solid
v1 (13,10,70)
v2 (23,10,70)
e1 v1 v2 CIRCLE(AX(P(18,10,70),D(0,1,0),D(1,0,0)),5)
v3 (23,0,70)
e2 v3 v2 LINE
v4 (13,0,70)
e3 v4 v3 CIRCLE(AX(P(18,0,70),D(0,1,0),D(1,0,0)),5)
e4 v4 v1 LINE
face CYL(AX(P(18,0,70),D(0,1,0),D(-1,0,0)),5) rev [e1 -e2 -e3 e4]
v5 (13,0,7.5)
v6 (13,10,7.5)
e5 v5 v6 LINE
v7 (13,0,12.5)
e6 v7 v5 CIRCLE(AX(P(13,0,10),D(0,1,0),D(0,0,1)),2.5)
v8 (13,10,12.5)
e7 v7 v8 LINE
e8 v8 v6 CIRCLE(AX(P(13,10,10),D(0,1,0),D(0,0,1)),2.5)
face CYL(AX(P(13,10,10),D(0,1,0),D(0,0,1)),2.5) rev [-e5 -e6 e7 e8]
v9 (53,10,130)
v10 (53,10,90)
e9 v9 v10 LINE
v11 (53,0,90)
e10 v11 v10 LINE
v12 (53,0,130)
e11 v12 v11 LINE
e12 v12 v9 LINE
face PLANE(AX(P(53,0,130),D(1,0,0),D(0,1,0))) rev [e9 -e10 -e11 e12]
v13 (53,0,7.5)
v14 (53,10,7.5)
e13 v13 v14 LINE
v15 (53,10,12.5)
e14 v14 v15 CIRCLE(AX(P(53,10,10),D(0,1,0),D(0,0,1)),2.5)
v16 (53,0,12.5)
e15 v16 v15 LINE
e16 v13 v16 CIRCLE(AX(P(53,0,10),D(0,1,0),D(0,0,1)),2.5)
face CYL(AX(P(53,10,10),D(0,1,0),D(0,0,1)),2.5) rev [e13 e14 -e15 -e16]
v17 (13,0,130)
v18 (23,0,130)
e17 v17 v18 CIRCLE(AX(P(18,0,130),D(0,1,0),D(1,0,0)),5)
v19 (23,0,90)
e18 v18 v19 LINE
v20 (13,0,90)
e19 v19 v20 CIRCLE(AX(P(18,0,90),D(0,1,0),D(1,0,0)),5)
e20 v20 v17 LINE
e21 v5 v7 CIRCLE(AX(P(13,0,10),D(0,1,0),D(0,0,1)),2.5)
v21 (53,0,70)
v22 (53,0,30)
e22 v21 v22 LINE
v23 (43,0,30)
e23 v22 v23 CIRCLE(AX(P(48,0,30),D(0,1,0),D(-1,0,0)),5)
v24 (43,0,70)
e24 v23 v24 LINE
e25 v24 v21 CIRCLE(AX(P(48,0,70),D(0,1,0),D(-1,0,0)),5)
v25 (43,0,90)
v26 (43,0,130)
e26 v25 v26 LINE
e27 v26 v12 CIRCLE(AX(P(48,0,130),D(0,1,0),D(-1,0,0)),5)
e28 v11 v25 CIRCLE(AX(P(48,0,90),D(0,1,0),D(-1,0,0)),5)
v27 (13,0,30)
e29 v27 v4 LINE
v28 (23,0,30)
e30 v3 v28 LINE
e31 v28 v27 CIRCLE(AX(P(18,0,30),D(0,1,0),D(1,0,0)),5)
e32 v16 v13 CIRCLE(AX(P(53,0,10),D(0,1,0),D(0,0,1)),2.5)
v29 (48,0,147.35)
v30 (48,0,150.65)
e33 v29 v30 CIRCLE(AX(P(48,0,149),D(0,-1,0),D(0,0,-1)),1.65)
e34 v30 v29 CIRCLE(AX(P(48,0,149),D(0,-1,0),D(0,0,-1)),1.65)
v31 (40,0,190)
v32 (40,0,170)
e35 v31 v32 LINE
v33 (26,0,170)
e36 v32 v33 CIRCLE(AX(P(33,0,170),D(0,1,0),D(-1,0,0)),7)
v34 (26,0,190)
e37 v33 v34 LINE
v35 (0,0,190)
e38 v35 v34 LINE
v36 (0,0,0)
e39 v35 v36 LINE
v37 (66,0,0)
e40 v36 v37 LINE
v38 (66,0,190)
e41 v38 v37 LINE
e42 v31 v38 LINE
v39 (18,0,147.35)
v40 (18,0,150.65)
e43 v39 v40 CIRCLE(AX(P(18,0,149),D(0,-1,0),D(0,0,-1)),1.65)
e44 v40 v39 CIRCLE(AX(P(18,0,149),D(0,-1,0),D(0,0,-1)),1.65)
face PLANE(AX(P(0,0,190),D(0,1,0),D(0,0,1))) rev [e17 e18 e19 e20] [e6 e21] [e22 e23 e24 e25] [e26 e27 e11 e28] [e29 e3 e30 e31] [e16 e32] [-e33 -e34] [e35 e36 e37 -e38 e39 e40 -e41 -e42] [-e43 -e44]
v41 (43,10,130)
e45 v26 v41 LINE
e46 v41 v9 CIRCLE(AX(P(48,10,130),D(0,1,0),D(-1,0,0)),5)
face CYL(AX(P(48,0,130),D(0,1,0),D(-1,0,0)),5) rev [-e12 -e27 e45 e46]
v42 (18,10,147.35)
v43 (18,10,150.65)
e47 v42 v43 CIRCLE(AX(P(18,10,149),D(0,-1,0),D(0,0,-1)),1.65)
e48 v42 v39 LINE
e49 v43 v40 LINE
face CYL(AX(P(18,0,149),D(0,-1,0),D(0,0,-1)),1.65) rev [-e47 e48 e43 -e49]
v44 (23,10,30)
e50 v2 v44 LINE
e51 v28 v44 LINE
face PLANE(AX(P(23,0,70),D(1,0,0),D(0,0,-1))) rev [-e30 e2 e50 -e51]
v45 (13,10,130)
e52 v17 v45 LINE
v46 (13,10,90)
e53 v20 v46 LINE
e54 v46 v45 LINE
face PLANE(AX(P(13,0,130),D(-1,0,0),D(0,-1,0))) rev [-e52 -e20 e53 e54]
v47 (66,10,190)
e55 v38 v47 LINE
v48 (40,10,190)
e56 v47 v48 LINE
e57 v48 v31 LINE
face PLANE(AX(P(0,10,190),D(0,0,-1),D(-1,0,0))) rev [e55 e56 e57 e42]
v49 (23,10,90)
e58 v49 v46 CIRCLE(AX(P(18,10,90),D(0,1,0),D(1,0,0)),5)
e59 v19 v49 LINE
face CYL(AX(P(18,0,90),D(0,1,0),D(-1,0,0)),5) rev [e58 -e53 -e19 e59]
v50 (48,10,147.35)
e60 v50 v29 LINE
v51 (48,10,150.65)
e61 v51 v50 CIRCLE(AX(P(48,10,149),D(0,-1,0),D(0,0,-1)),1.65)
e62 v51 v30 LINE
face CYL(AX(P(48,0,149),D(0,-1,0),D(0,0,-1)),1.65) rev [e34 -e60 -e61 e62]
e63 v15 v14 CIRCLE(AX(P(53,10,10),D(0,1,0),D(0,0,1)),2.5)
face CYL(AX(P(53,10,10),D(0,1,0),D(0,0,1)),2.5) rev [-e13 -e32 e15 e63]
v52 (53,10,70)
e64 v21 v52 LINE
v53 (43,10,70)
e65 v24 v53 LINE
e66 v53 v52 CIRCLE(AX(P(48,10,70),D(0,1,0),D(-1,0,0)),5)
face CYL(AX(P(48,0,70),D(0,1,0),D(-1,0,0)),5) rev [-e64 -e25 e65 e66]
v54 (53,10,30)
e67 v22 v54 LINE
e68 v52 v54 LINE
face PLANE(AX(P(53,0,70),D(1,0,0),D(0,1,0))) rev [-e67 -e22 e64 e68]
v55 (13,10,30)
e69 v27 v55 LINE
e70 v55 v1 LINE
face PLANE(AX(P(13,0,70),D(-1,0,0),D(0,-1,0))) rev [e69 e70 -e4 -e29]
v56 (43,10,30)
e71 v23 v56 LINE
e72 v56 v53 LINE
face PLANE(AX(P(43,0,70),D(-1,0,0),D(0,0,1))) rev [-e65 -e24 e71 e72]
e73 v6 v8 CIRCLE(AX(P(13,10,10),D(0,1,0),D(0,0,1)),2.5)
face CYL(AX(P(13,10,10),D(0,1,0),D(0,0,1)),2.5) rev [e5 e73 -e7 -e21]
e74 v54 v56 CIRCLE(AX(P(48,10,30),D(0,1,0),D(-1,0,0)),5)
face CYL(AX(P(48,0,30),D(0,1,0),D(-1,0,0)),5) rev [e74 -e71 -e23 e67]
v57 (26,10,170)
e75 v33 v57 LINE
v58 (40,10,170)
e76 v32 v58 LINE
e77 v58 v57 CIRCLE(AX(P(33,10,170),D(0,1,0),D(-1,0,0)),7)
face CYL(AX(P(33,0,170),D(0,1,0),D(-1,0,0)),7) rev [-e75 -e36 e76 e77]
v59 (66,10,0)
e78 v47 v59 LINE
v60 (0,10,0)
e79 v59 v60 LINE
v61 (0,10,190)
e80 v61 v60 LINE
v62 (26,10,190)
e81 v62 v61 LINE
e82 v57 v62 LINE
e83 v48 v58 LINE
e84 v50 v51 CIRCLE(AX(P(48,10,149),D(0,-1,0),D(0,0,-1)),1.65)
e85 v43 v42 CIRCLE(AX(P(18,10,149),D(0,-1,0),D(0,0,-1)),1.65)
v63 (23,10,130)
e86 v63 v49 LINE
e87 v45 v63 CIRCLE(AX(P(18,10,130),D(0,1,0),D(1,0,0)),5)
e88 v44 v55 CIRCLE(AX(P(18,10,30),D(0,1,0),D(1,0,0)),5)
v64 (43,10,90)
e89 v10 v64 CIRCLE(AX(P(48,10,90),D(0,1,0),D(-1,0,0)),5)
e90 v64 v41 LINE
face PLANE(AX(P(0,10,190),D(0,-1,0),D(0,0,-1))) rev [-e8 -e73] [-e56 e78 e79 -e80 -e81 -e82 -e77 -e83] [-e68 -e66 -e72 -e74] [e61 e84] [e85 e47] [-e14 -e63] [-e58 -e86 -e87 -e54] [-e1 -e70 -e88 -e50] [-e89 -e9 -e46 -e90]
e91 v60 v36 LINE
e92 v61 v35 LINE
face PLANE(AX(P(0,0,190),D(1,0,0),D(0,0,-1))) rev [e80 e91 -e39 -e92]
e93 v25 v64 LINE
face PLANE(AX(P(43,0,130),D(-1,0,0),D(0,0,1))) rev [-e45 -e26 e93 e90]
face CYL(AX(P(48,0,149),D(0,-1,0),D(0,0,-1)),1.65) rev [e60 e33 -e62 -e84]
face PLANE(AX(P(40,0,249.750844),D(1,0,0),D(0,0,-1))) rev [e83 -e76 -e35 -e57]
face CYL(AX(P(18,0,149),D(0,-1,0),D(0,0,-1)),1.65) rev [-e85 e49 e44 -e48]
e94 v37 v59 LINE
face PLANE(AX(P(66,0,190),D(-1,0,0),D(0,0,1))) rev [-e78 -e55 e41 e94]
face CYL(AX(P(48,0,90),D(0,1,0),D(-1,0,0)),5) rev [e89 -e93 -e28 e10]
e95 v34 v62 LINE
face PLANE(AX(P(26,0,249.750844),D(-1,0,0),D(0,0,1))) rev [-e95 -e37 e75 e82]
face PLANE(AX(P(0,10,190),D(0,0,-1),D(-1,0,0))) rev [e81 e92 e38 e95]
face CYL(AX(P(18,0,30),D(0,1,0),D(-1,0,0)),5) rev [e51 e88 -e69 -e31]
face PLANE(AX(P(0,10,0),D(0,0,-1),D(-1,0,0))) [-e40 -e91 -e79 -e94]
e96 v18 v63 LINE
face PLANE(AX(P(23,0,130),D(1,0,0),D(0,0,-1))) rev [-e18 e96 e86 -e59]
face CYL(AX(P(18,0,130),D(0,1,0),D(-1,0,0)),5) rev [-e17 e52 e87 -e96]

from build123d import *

# Parameters (mm, degrees)
SKETCH_1_W          = 66
SKETCH_1_H          = 10
EXTRUDE_1_DEPTH     = 190
CUT_EXTRUDE_2_DEPTH = 202.385203031
HOLE_WIZARD_M5_1_D  = 5
CUT_EXTRUDE_3_DEPTH = 202.385203031
HOLE_WIZARD_M4_1_D  = 3.3


with BuildPart() as part:
    # 草图1 → 拉伸1 (new body)
    with BuildSketch(Plane.XY):
        with Locations((33, 5)):
            Rectangle(SKETCH_1_W, SKETCH_1_H)
    extrude(amount=EXTRUDE_1_DEPTH)

    # 草图5 → 切除-拉伸2 (cut, through all)
    with BuildSketch(Plane(origin=(0, 10, 0), x_dir=(-1, 0, 0), z_dir=(0, 1, 0))):
        with BuildLine():
            Line((-43, 70), (-43, 30))
            ThreePointArc((-43, 30), (-48, 25), (-53, 30))
            Line((-53, 30), (-53, 70))
            ThreePointArc((-53, 70), (-48, 75), (-43, 70))
        make_face()
        with BuildLine():
            Line((-13, 70), (-13, 30))
            ThreePointArc((-13, 30), (-18, 25), (-23, 30))
            Line((-23, 30), (-23, 70))
            ThreePointArc((-23, 70), (-18, 75), (-13, 70))
        make_face()
        with BuildLine():
            Line((-43, 130), (-43, 90))
            ThreePointArc((-43, 90), (-48, 85), (-53, 90))
            Line((-53, 90), (-53, 130))
            ThreePointArc((-53, 130), (-48, 135), (-43, 130))
        make_face()
        with BuildLine():
            Line((-13, 130), (-13, 90))
            ThreePointArc((-13, 90), (-18, 85), (-23, 90))
            Line((-23, 90), (-23, 130))
            ThreePointArc((-23, 130), (-18, 135), (-13, 130))
        make_face()
    extrude(amount=-CUT_EXTRUDE_2_DEPTH, mode=Mode.SUBTRACT)

    # M5 螺纹孔1 (through all)
    with Locations(Plane(origin=(0, 10, 0), x_dir=(-1, 0, 0), z_dir=(0, 1, 0))):
        with Locations((-13, 10), (-53, 10)):
            Hole(HOLE_WIZARD_M5_1_D / 2)

    # 草图11 → 切除-拉伸3 (cut, through all)
    with BuildSketch(Plane(origin=(0, 10, 0), x_dir=(-1, 0, 0), z_dir=(0, 1, 0))):
        with BuildLine():
            Line((-40, 249.750844229), (-40, 170))
            ThreePointArc((-40, 170), (-33, 163), (-26, 170))
            Line((-26, 170), (-26, 249.750844229))
            Line((-26, 249.750844229), (-40, 249.750844229))
        make_face()
    extrude(amount=-CUT_EXTRUDE_3_DEPTH, mode=Mode.SUBTRACT)

    # M4 螺纹孔1 (through all)
    with Locations(Plane.XZ):
        with Locations((18, 149), (48, 149)):
            Hole(HOLE_WIZARD_M4_1_D / 2)


solid = part.part
